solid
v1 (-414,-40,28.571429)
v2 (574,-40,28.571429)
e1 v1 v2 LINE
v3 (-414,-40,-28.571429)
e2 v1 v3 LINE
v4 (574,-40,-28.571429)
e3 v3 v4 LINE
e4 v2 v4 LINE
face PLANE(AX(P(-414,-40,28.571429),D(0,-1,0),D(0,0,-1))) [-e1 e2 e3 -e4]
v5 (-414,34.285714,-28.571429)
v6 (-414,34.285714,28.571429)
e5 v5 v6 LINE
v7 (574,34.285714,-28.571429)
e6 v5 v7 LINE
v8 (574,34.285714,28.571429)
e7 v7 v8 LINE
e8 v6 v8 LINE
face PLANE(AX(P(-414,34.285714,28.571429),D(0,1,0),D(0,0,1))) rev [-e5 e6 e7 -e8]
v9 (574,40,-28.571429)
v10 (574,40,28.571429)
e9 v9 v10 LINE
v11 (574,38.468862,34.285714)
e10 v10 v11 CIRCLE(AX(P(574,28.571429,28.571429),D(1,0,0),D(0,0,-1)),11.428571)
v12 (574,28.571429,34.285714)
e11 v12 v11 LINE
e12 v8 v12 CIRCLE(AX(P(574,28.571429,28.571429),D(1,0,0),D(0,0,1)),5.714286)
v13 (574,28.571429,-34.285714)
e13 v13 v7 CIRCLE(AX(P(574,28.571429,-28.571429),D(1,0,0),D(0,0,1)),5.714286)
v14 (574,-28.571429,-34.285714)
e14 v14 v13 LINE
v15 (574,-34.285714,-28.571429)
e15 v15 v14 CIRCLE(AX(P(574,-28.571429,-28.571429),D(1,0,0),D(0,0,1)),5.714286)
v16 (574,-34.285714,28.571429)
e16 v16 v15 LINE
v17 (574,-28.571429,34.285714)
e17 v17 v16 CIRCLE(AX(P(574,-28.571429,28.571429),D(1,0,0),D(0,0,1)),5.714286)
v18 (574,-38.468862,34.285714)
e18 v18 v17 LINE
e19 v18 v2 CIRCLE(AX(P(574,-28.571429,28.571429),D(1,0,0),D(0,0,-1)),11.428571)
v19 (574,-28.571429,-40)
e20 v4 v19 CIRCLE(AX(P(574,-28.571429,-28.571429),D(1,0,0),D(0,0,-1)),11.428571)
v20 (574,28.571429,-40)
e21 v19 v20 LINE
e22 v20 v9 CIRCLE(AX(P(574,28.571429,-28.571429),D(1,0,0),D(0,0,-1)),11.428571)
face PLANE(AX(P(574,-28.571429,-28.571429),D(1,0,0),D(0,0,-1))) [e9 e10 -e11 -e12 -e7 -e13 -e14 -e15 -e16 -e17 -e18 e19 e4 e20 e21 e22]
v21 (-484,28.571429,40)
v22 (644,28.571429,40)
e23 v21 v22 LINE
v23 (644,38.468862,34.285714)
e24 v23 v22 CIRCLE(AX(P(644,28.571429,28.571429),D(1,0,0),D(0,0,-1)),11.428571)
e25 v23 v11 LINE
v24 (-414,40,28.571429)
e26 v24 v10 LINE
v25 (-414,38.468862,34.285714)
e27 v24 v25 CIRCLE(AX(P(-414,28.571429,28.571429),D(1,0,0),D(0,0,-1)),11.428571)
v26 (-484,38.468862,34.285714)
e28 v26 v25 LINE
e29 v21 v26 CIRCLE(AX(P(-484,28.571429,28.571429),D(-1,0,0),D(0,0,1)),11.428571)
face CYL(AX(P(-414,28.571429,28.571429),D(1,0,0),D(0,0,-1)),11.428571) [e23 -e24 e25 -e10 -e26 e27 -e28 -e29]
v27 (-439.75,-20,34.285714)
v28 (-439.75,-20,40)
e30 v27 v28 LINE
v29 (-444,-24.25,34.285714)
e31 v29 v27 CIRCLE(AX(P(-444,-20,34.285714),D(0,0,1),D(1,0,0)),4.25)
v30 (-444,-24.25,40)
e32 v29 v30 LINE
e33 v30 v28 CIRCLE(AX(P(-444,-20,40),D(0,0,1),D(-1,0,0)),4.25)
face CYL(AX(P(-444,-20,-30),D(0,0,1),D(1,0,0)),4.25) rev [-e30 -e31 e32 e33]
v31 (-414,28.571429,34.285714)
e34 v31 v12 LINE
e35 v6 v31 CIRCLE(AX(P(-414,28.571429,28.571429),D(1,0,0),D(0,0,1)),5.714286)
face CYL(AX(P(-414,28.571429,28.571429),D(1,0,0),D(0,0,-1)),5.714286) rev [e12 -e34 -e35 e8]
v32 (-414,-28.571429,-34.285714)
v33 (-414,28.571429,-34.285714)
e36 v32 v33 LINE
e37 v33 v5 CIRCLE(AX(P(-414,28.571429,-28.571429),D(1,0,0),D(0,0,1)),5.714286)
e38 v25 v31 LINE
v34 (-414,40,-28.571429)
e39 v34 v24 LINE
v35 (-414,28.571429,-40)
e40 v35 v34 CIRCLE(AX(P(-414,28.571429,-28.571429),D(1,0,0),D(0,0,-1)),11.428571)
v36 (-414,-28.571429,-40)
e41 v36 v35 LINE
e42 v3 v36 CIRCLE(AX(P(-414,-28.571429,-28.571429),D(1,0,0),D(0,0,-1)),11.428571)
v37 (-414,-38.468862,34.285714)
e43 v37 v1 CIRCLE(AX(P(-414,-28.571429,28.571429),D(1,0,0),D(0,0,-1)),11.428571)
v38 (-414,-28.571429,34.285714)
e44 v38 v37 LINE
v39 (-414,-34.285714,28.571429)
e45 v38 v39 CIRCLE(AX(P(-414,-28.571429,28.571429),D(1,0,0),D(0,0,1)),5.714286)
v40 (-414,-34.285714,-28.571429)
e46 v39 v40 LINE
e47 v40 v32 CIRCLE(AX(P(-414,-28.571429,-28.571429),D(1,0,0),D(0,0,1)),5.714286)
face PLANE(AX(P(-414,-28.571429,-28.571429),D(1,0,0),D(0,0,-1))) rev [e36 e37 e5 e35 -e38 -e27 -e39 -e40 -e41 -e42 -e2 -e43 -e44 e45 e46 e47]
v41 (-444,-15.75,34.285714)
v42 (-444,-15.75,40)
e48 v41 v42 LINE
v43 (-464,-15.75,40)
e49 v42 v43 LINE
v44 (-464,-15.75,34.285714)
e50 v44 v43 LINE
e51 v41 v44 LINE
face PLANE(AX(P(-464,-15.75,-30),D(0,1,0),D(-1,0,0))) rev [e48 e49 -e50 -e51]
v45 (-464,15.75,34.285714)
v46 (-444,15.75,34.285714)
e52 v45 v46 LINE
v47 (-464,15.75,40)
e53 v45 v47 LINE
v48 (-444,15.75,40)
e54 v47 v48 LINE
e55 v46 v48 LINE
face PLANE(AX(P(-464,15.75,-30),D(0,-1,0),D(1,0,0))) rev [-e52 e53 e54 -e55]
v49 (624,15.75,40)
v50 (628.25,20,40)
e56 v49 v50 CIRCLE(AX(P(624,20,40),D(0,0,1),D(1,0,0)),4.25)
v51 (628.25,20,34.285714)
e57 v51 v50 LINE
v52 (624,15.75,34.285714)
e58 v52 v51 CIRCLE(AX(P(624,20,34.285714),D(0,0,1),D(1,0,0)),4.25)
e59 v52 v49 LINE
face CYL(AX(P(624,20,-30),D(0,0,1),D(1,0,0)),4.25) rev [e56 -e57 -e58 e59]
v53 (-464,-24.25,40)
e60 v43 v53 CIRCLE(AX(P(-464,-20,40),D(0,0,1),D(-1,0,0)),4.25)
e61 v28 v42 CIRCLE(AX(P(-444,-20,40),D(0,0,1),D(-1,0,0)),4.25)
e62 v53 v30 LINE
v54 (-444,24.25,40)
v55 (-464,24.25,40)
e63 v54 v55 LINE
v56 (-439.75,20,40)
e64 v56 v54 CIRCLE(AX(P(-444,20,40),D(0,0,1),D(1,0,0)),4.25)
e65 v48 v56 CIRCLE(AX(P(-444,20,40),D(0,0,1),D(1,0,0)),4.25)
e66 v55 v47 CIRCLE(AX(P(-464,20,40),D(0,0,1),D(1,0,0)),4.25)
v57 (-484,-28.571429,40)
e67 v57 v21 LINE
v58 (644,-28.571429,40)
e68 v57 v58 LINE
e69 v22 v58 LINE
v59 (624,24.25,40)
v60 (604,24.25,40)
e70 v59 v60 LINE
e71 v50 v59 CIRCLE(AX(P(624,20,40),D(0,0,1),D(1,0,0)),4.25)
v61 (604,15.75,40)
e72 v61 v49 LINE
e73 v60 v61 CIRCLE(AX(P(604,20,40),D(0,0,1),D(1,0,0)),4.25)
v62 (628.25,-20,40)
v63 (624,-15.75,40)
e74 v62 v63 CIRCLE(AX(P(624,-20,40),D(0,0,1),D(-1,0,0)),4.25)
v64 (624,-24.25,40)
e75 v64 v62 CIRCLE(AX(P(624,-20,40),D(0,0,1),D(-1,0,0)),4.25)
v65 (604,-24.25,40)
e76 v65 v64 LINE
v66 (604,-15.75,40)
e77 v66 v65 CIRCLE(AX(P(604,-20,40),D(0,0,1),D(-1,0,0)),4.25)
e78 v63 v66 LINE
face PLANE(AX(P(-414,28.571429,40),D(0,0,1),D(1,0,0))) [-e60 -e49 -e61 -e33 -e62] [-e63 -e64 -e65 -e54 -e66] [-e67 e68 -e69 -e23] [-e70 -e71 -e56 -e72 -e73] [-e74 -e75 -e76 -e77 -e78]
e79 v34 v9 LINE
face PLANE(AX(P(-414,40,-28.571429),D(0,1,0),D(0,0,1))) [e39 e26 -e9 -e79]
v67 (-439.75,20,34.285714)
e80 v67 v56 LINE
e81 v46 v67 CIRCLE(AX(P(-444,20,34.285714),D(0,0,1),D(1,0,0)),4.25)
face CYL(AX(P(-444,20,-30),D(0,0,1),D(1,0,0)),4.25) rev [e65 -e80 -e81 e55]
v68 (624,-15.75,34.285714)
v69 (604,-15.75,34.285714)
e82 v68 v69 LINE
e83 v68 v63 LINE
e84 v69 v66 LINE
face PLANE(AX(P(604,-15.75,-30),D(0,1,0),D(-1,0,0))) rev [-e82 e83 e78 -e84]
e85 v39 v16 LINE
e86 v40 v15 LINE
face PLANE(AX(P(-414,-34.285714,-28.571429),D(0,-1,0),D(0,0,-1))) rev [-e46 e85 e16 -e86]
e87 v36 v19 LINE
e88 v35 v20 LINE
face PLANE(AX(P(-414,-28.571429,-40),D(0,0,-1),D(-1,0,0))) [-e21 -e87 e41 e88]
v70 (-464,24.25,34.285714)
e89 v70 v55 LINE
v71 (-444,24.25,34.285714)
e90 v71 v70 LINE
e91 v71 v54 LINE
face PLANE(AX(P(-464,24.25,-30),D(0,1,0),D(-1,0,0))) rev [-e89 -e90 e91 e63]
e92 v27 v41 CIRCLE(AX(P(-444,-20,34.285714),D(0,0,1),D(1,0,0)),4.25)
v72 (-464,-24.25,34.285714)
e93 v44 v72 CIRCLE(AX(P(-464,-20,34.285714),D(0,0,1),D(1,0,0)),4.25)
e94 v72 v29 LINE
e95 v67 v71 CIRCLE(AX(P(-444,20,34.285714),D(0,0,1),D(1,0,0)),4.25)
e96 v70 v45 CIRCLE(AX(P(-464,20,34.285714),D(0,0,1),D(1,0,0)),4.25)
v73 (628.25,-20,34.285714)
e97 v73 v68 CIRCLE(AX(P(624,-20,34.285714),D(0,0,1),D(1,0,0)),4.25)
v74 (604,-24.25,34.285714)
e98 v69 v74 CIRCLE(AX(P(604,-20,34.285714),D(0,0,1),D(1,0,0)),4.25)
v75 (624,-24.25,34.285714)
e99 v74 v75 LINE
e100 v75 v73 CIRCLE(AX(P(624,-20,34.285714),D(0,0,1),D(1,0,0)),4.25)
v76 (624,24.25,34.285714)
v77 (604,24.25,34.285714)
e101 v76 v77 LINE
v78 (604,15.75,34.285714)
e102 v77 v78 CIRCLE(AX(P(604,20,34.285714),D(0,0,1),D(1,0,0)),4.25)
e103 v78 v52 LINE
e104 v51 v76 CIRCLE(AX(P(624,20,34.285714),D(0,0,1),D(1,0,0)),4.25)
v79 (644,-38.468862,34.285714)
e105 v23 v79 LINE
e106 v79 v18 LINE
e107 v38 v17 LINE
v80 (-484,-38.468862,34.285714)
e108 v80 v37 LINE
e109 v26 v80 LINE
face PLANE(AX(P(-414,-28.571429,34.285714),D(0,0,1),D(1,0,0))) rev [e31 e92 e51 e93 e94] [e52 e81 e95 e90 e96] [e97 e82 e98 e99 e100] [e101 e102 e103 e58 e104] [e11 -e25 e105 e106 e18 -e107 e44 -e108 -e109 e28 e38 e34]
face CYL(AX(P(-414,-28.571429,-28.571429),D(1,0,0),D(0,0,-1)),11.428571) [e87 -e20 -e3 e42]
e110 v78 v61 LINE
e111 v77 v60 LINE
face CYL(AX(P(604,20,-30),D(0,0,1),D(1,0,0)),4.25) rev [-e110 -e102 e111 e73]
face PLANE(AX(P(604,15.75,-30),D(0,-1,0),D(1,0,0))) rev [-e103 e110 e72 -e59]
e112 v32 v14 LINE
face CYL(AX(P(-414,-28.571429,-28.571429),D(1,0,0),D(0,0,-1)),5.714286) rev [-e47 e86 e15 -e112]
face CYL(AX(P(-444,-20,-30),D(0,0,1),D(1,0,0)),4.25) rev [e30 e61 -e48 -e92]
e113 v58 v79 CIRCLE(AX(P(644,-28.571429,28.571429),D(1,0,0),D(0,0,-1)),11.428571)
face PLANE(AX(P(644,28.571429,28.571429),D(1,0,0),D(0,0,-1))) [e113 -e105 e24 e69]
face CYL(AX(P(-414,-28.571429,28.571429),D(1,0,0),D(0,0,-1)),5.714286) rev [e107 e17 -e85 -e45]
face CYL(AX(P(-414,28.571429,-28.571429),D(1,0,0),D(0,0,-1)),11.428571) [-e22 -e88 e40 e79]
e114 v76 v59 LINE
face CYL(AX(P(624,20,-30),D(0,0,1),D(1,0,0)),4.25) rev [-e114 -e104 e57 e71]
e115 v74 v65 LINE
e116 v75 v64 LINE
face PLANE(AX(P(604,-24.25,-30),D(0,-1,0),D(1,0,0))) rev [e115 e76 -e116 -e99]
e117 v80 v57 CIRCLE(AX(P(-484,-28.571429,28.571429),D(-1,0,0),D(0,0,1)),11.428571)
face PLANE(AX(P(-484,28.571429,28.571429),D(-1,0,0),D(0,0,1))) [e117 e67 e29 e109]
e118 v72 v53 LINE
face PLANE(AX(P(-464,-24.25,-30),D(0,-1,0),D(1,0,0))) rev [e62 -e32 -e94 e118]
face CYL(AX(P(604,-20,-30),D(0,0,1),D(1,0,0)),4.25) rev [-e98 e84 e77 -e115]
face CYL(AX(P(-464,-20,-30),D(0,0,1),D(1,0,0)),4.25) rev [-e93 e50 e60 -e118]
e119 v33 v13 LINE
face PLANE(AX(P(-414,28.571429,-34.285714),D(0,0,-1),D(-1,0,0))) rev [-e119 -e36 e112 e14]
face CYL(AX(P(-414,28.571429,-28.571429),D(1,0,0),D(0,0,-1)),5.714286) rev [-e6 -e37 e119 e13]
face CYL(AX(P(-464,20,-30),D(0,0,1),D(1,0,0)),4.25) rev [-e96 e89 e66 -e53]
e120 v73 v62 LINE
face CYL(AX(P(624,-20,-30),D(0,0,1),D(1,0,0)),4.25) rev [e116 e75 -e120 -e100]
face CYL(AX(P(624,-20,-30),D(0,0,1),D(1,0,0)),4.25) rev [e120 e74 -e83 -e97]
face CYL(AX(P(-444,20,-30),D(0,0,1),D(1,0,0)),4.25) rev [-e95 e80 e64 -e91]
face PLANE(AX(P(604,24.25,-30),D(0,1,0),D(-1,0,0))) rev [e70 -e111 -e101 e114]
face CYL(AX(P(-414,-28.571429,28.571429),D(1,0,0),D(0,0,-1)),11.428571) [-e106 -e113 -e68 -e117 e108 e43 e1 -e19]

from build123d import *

# Parameters (mm, degrees)
BOSS_EXTRUDE1_DEPTH = 988
BOSS_EXTRUDE2_START = 70
BOSS_EXTRUDE2_DEPTH = 70
BOSS_EXTRUDE3_DEPTH = 70
CUT_EXTRUDE1_DEPTH  = 70


with BuildPart() as part:
    # Sketch1 → Boss-Extrude1 (new body)
    with BuildSketch(Plane(origin=(574, 0, 0), x_dir=(0, 0, -1), z_dir=(1, 0, 0))):
        with BuildLine():
            Line((40, -28.571428571), (40, 28.571428571))
            ThreePointArc((40, 28.571428571), (36.652648928, 36.652648928), (28.571428571, 40))
            Line((28.571428571, 40), (-28.571428571, 40))
            ThreePointArc((-28.571428571, 40), (-36.652648928, 36.652648928), (-40, 28.571428571))
            Line((-40, 28.571428571), (-40, -28.571428571))
            ThreePointArc((-40, -28.571428571), (-36.652648928, -36.652648928), (-28.571428571, -40))
            Line((-28.571428571, -40), (28.571428571, -40))
            ThreePointArc((28.571428571, -40), (36.652648928, -36.652648928), (40, -28.571428571))
        make_face()
        with BuildLine():
            Line((-34.285714286, -28.571428571), (-34.285714286, 28.571428571))
            ThreePointArc((-34.285714286, 28.571428571), (-32.61203875, 32.61203875), (-28.571428571, 34.285714286))
            Line((-28.571428571, 34.285714286), (28.571428571, 34.285714286))
            ThreePointArc((28.571428571, 34.285714286), (32.61203875, 32.61203875), (34.285714286, 28.571428571))
            Line((34.285714286, 28.571428571), (34.285714286, -28.571428571))
            ThreePointArc((34.285714286, -28.571428571), (32.61203875, -32.61203875), (28.571428571, -34.285714286))
            Line((28.571428571, -34.285714286), (-28.571428571, -34.285714286))
            ThreePointArc((-28.571428571, -34.285714286), (-32.61203875, -32.61203875), (-34.285714286, -28.571428571))
        make_face(mode=Mode.SUBTRACT)
    extrude(amount=-BOSS_EXTRUDE1_DEPTH)

    # Sketch2 → Boss-Extrude2 (add)
    with BuildSketch(Plane(origin=(574, 0, 0), x_dir=(0, 0, -1), z_dir=(1, 0, 0)).offset(BOSS_EXTRUDE2_START)):
        with BuildLine():
            Line((-34.285714286, 28.571428571), (-34.285714286, 38.468861758))
            ThreePointArc((-34.285714286, 38.468861758), (-38.468861758, 34.285714286), (-40, 28.571428571))
            Line((-40, 28.571428571), (-40, -28.571428571))
            ThreePointArc((-40, -28.571428571), (-38.468861758, -34.285714286), (-34.285714286, -38.468861758))
            Line((-34.285714286, -38.468861758), (-34.285714286, -28.571428571))
            Line((-34.285714286, -28.571428571), (-34.285714286, 28.571428571))
        make_face()
    extrude(amount=-BOSS_EXTRUDE2_DEPTH)

    # Sketch3 → Boss-Extrude3 (add)
    with BuildSketch(Plane.ZY.offset(414)):
        with BuildLine():
            Line((34.285714286, -28.571428571), (34.285714286, -38.468861758))
            ThreePointArc((34.285714286, -38.468861758), (38.468861758, -34.285714286), (40, -28.571428571))
            Line((40, -28.571428571), (40, 28.571428571))
            ThreePointArc((40, 28.571428571), (38.468861758, 34.285714286), (34.285714286, 38.468861758))
            Line((34.285714286, 38.468861758), (34.285714286, -28.571428571))
        make_face()
    extrude(amount=BOSS_EXTRUDE3_DEPTH)

    # Sketch4 → Cut-Extrude1 (cut)
    with BuildSketch(Plane.XY.offset(40)):
        with BuildLine():
            Line((-464, 24.25), (-444, 24.25))
            ThreePointArc((-444, 24.25), (-439.75, 20), (-444, 15.75))
            Line((-444, 15.75), (-464, 15.75))
            ThreePointArc((-464, 15.75), (-468.25, 20), (-464, 24.25))
        make_face()
        with BuildLine():
            Line((-464, -24.25), (-444, -24.25))
            ThreePointArc((-444, -24.25), (-439.75, -20), (-444, -15.75))
            Line((-444, -15.75), (-464, -15.75))
            ThreePointArc((-464, -15.75), (-468.25, -20), (-464, -24.25))
        make_face()
        with BuildLine():
            Line((604, 24.25), (624, 24.25))
            ThreePointArc((624, 24.25), (628.25, 20), (624, 15.75))
            Line((624, 15.75), (604, 15.75))
            ThreePointArc((604, 15.75), (599.75, 20), (604, 24.25))
        make_face()
        with BuildLine():
            Line((604, -24.25), (624, -24.25))
            ThreePointArc((624, -24.25), (628.25, -20), (624, -15.75))
            Line((624, -15.75), (604, -15.75))
            ThreePointArc((604, -15.75), (599.75, -20), (604, -24.25))
        make_face()
    extrude(amount=-CUT_EXTRUDE1_DEPTH, mode=Mode.SUBTRACT)


solid = part.part
